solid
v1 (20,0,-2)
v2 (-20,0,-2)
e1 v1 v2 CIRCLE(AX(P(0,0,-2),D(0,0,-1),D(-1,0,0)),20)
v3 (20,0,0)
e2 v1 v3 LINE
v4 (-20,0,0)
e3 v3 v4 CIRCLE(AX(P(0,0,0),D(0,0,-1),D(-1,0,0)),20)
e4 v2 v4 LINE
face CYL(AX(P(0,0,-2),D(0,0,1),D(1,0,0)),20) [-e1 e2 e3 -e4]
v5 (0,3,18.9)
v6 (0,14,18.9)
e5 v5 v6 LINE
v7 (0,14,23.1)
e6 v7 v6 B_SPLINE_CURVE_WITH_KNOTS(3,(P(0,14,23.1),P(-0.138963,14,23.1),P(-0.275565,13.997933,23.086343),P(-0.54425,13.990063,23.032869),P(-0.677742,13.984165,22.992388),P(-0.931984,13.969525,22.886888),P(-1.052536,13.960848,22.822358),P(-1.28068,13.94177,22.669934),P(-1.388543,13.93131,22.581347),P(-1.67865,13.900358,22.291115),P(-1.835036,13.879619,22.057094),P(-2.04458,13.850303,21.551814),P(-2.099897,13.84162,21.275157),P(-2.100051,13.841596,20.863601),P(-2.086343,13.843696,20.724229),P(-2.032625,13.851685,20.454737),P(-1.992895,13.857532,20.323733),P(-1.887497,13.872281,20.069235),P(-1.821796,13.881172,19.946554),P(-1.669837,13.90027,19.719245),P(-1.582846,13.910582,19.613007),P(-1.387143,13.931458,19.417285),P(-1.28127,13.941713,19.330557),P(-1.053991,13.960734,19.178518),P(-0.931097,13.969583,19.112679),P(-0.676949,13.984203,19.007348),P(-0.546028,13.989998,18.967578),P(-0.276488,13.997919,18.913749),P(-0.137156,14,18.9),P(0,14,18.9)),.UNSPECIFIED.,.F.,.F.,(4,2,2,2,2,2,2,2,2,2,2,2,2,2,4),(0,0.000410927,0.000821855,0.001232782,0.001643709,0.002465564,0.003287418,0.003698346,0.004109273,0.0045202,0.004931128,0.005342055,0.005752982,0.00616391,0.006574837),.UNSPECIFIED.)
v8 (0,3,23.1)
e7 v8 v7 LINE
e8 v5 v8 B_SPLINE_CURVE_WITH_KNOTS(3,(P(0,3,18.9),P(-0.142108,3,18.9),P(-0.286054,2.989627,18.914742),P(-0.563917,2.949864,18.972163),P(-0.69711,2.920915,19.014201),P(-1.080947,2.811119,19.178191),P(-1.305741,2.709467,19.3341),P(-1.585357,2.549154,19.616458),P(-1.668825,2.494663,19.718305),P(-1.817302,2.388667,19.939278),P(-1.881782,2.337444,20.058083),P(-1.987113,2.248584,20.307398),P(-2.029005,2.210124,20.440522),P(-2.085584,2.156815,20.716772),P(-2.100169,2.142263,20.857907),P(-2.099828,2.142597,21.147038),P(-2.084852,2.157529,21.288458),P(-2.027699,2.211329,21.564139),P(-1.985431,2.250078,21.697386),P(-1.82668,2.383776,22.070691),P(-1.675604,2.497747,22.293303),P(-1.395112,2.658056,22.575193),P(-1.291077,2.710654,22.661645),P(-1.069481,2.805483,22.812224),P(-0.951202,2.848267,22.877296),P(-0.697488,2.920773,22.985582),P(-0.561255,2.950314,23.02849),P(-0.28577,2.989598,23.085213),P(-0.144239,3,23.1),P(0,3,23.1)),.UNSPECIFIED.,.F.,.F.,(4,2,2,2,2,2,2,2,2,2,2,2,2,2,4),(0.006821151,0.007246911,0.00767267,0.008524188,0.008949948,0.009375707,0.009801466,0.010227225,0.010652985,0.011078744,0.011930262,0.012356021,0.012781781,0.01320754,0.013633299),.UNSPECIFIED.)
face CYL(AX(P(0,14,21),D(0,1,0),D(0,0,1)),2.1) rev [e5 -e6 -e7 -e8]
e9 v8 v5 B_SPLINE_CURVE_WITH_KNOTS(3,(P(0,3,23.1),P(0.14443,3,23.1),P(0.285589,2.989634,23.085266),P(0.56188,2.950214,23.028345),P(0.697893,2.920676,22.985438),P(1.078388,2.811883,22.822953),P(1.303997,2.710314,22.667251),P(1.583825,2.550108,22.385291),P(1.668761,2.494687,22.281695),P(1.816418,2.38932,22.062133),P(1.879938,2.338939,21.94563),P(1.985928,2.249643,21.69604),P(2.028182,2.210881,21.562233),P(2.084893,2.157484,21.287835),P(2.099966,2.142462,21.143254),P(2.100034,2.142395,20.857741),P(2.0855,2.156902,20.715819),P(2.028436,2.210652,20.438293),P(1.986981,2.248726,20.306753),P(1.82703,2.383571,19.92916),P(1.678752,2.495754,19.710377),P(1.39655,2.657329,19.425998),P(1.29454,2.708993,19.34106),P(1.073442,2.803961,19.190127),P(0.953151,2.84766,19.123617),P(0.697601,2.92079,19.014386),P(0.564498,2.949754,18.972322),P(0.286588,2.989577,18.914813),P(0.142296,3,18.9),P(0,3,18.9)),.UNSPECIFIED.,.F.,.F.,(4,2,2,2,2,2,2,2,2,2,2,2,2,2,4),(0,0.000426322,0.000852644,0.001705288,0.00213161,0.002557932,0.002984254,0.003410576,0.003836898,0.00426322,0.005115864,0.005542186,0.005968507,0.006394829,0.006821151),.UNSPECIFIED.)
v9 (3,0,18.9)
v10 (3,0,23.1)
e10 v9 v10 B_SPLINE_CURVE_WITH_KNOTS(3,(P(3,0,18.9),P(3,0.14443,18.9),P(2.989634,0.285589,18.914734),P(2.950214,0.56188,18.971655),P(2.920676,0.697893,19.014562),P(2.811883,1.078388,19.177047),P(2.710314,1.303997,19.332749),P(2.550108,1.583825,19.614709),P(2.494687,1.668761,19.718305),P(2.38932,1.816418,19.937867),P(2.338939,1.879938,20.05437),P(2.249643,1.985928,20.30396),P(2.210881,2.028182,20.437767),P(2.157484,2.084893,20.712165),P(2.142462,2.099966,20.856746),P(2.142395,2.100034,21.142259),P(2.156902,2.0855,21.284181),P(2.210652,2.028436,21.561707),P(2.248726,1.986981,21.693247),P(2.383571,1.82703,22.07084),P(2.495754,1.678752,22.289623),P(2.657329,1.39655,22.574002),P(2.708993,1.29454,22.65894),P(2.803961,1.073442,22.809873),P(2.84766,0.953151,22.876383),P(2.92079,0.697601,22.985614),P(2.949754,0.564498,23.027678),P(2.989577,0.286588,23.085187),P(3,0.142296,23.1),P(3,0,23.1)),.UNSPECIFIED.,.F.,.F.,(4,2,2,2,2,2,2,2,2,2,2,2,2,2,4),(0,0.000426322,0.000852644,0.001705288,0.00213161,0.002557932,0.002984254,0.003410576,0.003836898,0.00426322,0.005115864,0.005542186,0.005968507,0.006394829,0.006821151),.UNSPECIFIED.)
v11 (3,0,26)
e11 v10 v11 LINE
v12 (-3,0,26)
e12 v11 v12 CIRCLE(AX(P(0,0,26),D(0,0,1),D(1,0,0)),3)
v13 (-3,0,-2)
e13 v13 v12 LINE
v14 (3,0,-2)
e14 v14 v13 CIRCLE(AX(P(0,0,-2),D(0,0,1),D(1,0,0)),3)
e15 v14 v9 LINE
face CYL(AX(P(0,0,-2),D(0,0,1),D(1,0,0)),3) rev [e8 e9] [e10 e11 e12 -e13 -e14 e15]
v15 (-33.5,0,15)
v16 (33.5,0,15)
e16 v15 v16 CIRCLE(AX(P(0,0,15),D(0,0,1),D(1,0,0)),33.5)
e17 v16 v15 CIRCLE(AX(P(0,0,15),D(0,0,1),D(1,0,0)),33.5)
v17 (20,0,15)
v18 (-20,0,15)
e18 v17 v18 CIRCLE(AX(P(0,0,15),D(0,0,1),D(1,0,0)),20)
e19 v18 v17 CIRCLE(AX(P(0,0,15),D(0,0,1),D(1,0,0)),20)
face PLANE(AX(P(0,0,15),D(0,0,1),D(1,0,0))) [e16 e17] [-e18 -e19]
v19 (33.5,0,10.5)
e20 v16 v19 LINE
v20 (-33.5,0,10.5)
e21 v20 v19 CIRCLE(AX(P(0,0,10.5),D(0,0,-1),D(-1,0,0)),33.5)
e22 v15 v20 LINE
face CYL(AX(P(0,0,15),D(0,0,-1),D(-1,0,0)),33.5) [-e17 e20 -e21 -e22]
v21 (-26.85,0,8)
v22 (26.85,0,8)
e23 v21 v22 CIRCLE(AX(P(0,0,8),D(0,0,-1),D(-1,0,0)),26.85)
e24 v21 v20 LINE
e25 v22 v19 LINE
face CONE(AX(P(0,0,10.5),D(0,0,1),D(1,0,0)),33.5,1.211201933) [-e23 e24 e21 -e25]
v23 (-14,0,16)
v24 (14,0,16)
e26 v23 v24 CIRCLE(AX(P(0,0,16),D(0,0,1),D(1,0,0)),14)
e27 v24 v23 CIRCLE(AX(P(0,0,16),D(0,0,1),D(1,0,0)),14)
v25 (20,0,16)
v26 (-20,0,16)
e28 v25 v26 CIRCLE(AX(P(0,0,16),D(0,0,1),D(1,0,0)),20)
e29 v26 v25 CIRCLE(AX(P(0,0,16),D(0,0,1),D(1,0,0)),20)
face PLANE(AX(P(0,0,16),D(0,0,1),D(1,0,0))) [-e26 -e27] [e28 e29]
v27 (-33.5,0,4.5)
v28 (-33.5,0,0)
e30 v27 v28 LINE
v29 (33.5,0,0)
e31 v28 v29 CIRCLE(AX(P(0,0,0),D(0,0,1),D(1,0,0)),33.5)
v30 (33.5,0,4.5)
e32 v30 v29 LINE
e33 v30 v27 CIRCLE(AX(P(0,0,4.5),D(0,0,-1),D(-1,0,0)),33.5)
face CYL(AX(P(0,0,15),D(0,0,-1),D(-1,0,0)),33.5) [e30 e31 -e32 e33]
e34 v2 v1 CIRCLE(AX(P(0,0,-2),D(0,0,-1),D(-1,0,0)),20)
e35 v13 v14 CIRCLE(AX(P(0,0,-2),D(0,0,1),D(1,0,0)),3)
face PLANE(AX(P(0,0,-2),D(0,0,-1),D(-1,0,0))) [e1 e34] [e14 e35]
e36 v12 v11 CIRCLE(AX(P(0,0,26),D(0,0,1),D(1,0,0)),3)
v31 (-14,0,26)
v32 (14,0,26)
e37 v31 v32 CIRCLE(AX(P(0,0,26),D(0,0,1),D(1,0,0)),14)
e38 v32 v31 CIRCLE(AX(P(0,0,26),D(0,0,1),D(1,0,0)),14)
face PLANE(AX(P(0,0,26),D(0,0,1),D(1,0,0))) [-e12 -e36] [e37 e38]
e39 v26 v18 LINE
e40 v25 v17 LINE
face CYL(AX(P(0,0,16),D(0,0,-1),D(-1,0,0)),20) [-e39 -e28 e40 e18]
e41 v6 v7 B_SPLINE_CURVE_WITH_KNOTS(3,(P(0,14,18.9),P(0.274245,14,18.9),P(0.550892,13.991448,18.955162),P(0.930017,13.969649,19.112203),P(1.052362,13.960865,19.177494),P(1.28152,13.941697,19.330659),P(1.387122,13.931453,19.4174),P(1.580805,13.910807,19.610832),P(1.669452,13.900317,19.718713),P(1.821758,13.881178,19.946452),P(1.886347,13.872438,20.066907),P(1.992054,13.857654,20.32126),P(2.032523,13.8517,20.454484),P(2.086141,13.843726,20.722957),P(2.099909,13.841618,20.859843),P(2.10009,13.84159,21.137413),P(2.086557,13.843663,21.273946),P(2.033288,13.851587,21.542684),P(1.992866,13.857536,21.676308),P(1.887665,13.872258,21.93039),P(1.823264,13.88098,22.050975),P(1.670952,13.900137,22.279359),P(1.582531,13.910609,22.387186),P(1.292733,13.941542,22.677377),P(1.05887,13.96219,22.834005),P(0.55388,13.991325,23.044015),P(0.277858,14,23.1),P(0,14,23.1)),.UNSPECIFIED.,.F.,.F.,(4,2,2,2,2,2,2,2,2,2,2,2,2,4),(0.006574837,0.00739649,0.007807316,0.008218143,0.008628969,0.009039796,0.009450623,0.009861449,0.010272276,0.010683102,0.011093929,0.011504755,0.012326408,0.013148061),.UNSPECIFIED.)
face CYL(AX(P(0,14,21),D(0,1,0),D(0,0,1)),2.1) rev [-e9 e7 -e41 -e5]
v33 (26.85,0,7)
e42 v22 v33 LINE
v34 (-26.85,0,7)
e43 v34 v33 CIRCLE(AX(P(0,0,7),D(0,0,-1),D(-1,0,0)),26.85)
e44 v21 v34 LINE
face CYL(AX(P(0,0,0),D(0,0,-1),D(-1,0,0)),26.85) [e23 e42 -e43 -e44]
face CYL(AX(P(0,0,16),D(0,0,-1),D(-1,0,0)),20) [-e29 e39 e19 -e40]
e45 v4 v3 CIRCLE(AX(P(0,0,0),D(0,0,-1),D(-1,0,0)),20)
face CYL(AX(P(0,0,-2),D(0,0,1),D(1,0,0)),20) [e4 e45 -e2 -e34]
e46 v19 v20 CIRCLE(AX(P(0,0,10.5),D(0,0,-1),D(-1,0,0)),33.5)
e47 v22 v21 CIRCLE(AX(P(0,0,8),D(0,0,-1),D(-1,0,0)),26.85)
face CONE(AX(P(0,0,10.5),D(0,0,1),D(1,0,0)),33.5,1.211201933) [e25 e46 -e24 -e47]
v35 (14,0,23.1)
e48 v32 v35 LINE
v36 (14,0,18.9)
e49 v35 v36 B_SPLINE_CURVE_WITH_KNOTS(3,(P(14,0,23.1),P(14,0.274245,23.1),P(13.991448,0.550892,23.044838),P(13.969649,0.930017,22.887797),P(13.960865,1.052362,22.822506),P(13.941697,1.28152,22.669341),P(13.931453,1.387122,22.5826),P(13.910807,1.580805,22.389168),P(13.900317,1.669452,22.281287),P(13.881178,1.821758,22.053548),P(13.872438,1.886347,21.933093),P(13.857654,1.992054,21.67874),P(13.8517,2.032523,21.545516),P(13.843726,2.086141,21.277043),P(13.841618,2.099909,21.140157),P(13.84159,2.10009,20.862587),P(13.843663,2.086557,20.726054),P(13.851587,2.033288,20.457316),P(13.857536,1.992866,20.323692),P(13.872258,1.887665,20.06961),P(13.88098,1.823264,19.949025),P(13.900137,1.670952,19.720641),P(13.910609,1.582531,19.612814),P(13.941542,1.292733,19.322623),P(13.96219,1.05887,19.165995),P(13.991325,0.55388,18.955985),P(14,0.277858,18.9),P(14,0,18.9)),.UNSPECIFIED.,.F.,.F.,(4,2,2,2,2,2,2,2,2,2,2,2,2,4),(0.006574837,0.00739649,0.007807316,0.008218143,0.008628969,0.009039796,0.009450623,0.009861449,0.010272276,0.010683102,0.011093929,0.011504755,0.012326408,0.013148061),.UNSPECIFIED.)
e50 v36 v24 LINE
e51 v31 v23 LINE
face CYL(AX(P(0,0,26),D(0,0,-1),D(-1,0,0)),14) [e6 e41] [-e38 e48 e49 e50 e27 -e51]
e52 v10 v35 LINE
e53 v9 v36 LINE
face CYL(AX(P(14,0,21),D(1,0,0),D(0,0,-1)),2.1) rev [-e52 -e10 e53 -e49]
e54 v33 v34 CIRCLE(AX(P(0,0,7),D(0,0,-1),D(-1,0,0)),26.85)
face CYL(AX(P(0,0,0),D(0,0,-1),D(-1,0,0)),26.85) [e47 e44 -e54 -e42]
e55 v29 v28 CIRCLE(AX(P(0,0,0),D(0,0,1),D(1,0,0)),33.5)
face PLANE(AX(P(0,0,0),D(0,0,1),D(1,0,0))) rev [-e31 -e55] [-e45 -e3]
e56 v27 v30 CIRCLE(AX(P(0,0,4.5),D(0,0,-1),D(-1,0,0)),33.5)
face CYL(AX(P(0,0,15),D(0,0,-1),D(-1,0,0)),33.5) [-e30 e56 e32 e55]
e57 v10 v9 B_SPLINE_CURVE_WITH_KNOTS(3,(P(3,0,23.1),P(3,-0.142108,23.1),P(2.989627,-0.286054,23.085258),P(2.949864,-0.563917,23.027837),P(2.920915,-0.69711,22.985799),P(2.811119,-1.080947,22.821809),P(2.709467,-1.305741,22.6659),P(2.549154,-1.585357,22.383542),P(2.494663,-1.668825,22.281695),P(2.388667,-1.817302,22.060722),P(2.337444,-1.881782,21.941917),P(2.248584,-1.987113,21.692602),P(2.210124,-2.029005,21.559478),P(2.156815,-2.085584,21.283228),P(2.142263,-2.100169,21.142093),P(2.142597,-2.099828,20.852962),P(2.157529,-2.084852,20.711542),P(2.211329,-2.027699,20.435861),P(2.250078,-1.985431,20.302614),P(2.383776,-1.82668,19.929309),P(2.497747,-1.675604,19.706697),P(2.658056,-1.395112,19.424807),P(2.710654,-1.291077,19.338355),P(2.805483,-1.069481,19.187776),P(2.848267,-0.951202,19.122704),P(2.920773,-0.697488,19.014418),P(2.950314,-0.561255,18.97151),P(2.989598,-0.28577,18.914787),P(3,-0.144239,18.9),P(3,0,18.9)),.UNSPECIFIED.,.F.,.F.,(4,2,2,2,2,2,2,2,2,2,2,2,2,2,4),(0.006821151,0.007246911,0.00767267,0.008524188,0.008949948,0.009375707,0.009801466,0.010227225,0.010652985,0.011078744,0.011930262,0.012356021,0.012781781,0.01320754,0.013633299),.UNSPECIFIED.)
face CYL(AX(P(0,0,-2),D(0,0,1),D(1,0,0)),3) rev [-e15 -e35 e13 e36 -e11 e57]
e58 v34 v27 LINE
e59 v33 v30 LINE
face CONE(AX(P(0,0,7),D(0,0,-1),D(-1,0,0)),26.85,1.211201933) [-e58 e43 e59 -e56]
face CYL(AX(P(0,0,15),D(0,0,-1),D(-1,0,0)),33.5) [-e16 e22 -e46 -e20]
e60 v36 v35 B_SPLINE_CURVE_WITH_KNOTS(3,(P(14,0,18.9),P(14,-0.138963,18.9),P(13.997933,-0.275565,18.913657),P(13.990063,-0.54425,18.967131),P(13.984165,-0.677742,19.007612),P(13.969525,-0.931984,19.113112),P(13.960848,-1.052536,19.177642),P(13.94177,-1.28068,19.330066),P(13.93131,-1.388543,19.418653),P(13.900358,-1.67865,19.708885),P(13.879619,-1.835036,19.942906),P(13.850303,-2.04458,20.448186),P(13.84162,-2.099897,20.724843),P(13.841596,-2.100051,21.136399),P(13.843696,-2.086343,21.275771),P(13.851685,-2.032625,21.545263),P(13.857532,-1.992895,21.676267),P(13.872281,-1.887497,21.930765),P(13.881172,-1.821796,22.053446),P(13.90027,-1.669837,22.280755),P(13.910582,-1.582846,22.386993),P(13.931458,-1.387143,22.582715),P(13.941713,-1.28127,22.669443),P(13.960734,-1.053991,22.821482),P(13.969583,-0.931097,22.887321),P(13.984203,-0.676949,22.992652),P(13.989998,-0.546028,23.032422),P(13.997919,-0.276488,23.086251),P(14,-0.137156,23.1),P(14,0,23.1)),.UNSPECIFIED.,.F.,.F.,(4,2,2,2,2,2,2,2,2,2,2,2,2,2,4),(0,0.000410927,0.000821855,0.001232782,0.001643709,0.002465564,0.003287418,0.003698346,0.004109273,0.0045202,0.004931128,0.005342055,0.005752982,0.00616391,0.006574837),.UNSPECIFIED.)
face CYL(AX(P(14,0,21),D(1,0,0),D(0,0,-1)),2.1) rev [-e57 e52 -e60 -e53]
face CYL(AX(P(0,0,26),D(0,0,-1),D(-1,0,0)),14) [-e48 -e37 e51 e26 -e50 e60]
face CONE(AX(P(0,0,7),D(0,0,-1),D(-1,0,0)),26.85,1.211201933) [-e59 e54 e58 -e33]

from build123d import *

# Parameters (mm, degrees)
SKETCH1_R                       = 33.5
BOSS_EXTRUDE1_DEPTH             = 15
SKETCH4_R                       = 14
BOSS_EXTRUDE2_DEPTH             = 11
SKETCH3_R                       = 20
BOSS_EXTRUDE4_DEPTH             = 2
BOSS_EXTRUDE3_START             = 1
SKETCH2_R                       = 20
BOSS_EXTRUDE3_DEPTH             = 1
SKETCH5_R                       = 3
CUT_EXTRUDE3_DEPTH              = 56.031808984
M5_TAPPED_HOLE1_D               = 4.2
M5_TAPPED_HOLE1_DEPTH           = 13
M5_TAPPED_HOLE1_TIP             = 1.2618073
M5_TAPPED_HOLE1_ON_FACE_2_D     = 4.2
M5_TAPPED_HOLE1_ON_FACE_2_DEPTH = 13
M5_TAPPED_HOLE1_ON_FACE_2_TIP   = 1.2618073


with BuildPart() as part:
    # Sketch1 → Boss-Extrude1 (new body)
    with BuildSketch(Plane.XY):
        Circle(SKETCH1_R)
    extrude(amount=BOSS_EXTRUDE1_DEPTH)

    # Sketch4 → Boss-Extrude2 (add)
    with BuildSketch(Plane.XY.offset(15)):
        Circle(SKETCH4_R)
    extrude(amount=BOSS_EXTRUDE2_DEPTH)

    # Sketch3 → Boss-Extrude4 (add)
    with BuildSketch(Plane(origin=(0, 0, 0), x_dir=(-1, 0, 0), z_dir=(0, 0, -1))):
        Circle(SKETCH3_R)
    extrude(amount=BOSS_EXTRUDE4_DEPTH)

    # Sketch2 → Boss-Extrude3 (add)
    with BuildSketch(Plane.XY.offset(15).offset(BOSS_EXTRUDE3_START)):
        with Locations(Location((0, 0, 0), (0, 0, 180))):
            Circle(SKETCH2_R)
    extrude(amount=-BOSS_EXTRUDE3_DEPTH)

    # Sketch5 → Cut-Extrude3 (cut, through all)
    with BuildSketch(Plane.XY.offset(26)):
        Circle(SKETCH5_R)
    extrude(amount=-CUT_EXTRUDE3_DEPTH, mode=Mode.SUBTRACT)

    # Sketch7 → Cut-Revolve1 (revolve, cut)
    with BuildSketch(Plane(origin=(0, 0, 0), x_dir=(0, 0, -1), z_dir=(1, 0, 0)), mode=Mode.PRIVATE) as cut_revolve1_sk:
        Polygon((-8, 26.85), (-7, 26.85), (-4.5, 33.5), (-10.5, 33.5), align=None)
    revolve(cut_revolve1_sk.sketch.rotate(Axis((0, 0, 0), (0, 0, 1)), 90), axis=Axis((0, 0, 0), (0, 0, 1)), mode=Mode.SUBTRACT)

    # M5 Tapped Hole1
    with Locations(Plane(origin=(0, 14, 21), x_dir=(1, 0, 0), z_dir=(0, 1, 0))):
        with Locations((0, 0)):
            Hole(M5_TAPPED_HOLE1_D / 2, depth=M5_TAPPED_HOLE1_DEPTH)
            with Locations((0, 0, -(M5_TAPPED_HOLE1_DEPTH + M5_TAPPED_HOLE1_TIP / 2))):  # 118° drill point
                Cone(0, M5_TAPPED_HOLE1_D / 2, M5_TAPPED_HOLE1_TIP, mode=Mode.SUBTRACT)

    # M5 Tapped Hole1 on face 2
    with Locations(Plane(origin=(14, 0, 21), x_dir=(0, 0, 1), z_dir=(1, 0, 0))):
        with Locations((0, 0)):
            Hole(M5_TAPPED_HOLE1_ON_FACE_2_D / 2, depth=M5_TAPPED_HOLE1_ON_FACE_2_DEPTH)
            with Locations((0, 0, -(M5_TAPPED_HOLE1_ON_FACE_2_DEPTH + M5_TAPPED_HOLE1_ON_FACE_2_TIP / 2))):  # 118° drill point
                Cone(0, M5_TAPPED_HOLE1_ON_FACE_2_D / 2, M5_TAPPED_HOLE1_ON_FACE_2_TIP, mode=Mode.SUBTRACT)


solid = part.part
